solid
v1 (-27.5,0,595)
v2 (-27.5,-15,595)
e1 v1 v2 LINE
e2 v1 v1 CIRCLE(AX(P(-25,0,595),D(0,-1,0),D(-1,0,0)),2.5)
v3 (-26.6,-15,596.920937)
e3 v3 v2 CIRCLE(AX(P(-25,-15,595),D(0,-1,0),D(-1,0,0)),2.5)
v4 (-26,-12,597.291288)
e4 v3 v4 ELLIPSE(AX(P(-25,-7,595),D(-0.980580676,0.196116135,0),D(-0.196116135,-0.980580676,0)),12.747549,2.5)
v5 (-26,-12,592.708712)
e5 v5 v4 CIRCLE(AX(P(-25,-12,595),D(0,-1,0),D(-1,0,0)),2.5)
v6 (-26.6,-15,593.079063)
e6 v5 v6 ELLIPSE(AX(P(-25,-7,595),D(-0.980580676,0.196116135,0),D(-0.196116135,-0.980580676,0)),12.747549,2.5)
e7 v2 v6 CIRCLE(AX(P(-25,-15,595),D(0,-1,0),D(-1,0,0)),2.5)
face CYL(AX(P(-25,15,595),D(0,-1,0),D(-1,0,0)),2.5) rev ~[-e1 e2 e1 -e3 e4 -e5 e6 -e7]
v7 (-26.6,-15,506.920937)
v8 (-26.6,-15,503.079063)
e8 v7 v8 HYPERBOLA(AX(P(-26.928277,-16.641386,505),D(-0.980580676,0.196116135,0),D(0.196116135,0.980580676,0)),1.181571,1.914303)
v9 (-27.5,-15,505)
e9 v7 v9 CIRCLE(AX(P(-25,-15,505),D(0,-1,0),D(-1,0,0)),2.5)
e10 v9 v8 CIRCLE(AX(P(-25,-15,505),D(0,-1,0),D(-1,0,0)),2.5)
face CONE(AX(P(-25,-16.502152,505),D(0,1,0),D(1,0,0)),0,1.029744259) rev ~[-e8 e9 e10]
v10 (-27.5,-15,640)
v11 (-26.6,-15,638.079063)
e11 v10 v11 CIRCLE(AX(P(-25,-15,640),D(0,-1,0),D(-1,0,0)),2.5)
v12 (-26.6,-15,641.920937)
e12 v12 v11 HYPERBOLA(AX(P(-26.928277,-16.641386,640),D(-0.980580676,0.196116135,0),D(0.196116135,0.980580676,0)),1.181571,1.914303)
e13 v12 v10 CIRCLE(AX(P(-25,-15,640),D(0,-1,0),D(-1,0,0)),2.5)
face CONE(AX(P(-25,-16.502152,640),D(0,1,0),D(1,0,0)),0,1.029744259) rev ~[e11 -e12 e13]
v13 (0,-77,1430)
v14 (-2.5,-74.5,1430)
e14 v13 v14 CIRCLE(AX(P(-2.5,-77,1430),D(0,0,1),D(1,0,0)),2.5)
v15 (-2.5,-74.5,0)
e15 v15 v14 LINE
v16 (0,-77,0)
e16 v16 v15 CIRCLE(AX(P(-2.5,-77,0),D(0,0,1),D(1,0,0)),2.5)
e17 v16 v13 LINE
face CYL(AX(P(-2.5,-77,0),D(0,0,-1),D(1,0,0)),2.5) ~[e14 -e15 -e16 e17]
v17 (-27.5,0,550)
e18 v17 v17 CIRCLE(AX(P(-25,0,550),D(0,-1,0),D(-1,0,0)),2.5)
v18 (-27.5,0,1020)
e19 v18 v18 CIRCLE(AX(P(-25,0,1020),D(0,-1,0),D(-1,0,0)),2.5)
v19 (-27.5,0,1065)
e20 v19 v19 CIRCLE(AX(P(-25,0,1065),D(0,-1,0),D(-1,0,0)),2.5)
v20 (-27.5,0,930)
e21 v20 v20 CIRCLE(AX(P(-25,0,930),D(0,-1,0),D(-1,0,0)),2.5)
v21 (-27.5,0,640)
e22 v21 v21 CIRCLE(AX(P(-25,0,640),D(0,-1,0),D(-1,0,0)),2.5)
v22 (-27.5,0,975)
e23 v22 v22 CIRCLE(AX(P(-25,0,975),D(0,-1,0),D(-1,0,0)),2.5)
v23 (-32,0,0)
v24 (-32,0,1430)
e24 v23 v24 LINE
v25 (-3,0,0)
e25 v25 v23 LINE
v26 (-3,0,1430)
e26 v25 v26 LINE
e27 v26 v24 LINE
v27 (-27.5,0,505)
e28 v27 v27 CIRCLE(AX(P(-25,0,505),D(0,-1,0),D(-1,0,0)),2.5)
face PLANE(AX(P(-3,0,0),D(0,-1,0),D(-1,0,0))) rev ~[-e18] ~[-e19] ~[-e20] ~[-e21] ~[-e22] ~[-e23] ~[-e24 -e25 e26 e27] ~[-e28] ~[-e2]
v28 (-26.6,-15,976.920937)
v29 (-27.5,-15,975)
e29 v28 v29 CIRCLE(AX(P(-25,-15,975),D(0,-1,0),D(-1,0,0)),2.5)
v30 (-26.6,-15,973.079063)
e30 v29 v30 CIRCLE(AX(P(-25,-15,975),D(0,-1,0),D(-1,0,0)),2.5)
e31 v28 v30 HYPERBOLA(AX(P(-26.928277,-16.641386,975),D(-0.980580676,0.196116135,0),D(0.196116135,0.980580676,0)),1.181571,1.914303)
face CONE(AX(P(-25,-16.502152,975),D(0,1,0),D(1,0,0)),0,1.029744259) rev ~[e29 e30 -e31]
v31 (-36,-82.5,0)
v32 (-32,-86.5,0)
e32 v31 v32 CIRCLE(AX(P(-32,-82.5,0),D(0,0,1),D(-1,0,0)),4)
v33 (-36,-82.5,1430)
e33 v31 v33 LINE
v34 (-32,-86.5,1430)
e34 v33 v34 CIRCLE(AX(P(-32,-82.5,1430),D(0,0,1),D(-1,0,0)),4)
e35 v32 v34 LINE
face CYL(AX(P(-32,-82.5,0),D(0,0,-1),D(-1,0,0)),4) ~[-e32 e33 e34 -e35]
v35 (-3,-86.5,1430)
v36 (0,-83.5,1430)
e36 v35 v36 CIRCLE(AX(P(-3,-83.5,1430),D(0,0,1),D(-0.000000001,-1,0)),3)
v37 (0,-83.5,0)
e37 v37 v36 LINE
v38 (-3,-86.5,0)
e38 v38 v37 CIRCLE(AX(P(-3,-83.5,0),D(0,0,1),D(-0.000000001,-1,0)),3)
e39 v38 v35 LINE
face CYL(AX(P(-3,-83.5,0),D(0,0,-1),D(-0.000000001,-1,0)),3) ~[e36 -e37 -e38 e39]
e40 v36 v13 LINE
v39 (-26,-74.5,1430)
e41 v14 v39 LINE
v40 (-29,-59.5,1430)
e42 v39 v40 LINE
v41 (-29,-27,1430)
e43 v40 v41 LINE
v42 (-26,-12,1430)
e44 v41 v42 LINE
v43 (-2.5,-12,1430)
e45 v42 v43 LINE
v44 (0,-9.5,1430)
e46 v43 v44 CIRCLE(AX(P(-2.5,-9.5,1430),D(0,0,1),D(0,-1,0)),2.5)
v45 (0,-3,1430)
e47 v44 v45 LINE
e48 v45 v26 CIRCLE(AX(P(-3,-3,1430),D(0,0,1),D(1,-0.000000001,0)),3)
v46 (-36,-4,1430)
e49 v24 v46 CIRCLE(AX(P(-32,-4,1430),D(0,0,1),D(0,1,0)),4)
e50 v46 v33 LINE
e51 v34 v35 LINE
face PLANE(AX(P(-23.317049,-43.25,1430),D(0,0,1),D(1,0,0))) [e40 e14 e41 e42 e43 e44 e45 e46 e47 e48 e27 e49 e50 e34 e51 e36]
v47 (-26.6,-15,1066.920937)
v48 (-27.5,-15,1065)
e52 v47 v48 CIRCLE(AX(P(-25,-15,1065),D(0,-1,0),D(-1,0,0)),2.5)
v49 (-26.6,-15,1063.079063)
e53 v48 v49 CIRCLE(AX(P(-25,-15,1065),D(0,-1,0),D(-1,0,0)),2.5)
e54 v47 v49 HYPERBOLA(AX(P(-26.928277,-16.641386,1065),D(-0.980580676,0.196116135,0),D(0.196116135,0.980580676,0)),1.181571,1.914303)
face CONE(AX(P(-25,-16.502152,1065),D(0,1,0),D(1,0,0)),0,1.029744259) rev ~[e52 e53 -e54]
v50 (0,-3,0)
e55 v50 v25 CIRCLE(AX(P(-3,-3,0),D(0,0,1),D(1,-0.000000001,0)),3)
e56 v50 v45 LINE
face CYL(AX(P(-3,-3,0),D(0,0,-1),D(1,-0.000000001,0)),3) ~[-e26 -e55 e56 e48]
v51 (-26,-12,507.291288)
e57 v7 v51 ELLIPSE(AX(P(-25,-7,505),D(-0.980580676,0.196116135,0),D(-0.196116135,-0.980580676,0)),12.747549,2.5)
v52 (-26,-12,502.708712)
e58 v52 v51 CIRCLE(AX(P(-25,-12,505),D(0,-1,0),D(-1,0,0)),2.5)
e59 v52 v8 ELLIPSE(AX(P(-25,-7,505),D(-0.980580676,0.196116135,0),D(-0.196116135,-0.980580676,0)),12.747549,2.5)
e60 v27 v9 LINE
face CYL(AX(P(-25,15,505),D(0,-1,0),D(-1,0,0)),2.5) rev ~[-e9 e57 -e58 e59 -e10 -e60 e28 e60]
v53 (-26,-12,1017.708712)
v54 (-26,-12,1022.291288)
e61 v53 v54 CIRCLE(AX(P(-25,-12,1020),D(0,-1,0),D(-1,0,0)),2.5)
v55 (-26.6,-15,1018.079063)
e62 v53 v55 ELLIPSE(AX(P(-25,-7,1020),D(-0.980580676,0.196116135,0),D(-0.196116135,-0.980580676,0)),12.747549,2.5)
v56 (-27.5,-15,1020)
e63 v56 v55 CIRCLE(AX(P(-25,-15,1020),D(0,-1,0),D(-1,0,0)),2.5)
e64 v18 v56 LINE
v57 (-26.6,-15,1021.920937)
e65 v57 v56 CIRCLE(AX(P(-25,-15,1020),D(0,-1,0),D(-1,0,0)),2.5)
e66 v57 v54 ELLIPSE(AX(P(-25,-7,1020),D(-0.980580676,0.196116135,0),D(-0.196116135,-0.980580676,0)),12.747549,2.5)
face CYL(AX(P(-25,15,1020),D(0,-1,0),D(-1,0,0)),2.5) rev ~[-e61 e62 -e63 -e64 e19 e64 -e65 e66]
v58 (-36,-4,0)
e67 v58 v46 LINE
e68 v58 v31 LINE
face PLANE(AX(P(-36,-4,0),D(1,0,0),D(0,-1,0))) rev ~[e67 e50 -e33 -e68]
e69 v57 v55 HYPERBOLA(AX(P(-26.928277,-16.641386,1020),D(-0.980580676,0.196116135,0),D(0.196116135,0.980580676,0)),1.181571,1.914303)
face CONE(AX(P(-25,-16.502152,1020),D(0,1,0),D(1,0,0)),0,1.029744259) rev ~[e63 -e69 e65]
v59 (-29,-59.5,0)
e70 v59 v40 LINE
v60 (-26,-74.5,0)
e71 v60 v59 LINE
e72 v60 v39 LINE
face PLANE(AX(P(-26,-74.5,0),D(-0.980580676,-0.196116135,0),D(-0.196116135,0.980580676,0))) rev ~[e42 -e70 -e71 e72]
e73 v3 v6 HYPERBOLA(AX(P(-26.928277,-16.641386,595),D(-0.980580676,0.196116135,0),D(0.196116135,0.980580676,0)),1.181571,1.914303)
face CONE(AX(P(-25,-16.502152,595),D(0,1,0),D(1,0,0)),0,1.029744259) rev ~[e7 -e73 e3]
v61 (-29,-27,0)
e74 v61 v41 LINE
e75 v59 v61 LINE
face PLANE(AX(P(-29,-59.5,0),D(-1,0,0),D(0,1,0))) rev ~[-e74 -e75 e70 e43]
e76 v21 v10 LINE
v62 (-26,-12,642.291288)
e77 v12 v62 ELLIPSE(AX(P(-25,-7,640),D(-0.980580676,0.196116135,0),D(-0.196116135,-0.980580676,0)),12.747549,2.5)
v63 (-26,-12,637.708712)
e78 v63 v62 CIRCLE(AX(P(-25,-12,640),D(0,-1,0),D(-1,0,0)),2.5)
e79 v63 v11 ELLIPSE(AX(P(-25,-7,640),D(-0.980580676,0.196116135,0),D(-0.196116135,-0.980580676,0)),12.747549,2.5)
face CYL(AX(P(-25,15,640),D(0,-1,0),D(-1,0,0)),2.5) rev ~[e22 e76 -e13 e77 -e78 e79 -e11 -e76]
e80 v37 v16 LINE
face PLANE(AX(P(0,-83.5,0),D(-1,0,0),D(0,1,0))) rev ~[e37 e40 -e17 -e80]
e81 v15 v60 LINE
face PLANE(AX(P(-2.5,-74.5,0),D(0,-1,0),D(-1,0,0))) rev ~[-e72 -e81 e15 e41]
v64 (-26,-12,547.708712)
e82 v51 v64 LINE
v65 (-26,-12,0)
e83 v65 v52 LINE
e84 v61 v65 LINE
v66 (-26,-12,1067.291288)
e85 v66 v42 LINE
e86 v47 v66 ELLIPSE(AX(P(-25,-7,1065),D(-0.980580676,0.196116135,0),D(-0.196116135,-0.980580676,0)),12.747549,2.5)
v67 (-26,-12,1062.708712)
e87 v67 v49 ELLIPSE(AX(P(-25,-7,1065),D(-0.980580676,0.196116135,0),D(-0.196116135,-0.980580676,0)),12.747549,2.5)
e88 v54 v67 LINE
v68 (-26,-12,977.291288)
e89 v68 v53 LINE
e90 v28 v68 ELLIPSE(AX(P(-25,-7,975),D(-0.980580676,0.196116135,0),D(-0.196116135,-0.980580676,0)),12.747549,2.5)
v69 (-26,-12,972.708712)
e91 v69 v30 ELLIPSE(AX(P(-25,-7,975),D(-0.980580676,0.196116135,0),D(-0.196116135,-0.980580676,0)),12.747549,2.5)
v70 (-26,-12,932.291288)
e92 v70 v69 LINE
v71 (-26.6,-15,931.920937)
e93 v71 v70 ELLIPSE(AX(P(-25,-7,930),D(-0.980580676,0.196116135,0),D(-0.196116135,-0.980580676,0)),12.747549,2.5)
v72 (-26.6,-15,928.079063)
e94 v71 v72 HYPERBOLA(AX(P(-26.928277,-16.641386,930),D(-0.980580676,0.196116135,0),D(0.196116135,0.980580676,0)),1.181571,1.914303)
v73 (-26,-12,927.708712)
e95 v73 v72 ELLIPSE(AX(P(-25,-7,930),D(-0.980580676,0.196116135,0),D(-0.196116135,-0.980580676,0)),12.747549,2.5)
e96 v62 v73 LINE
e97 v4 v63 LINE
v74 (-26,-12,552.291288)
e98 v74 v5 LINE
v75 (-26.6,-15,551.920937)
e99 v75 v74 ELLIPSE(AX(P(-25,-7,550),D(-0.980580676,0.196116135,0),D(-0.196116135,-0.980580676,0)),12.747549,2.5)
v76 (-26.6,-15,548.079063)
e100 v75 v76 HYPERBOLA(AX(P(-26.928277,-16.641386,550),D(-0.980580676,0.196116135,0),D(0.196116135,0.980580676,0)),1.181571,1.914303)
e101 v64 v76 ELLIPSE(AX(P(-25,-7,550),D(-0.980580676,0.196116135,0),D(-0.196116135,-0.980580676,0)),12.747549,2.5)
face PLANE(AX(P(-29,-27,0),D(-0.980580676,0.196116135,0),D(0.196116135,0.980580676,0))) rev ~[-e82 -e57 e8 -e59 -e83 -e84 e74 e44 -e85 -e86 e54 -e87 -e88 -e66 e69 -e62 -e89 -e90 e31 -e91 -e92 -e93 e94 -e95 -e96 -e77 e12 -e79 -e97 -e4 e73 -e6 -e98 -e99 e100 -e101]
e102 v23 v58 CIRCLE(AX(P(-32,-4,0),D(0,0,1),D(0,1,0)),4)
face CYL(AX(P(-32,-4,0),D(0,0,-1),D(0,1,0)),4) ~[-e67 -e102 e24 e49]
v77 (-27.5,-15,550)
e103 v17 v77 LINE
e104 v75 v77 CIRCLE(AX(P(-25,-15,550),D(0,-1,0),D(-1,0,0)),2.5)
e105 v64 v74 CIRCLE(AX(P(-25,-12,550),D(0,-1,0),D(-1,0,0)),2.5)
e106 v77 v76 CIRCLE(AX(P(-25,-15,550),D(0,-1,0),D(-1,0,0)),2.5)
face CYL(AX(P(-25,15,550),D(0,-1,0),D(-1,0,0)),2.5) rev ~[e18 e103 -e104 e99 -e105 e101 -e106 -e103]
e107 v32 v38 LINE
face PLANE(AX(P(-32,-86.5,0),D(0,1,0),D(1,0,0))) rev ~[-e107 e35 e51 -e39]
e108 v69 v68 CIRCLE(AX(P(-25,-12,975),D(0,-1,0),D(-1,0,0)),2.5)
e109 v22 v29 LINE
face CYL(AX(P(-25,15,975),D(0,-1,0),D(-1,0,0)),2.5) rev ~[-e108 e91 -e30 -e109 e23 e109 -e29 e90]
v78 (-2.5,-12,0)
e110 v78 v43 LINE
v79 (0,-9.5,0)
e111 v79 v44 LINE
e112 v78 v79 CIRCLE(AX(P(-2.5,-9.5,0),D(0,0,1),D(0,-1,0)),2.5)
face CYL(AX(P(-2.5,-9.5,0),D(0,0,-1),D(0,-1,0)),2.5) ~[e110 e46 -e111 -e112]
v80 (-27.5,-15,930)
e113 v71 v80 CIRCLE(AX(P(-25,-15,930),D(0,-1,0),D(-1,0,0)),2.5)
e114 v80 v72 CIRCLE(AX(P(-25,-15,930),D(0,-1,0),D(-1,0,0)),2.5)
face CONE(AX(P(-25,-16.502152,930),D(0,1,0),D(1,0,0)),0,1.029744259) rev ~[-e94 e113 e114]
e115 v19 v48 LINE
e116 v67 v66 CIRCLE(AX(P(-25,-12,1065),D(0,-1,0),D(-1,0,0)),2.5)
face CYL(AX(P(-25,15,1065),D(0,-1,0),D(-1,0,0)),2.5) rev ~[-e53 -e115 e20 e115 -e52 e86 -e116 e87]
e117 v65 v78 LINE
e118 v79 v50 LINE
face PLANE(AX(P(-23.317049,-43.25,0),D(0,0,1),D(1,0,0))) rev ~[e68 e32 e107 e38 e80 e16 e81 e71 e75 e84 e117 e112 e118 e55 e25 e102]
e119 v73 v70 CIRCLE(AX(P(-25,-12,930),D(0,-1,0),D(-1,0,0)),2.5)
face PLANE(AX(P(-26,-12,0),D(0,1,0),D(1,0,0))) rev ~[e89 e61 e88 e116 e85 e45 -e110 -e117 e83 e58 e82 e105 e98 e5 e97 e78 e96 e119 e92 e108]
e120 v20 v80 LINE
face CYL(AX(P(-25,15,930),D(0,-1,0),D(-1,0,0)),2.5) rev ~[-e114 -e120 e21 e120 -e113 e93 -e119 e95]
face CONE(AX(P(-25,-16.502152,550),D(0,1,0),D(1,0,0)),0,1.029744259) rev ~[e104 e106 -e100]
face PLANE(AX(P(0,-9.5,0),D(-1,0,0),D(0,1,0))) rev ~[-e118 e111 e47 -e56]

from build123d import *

# Parameters (mm, degrees)
BOSS_EXTRUDE1_DEPTH   = 1430
M6_TAPPED_HOLE1_D     = 5
M6_TAPPED_HOLE1_DEPTH = 15
M6_TAPPED_HOLE1_TIP   = 1.502151548


with BuildPart() as part:
    # Sketch1 → Boss-Extrude1 (new body)
    with BuildSketch(Plane.XY):
        with BuildLine():
            Line((-3, 0), (-32, 0))
            ThreePointArc((-32, 0), (-34.828427125, -1.171572875), (-36, -4))
            Line((-36, -4), (-36, -82.5))
            ThreePointArc((-36, -82.5), (-34.828427125, -85.328427125), (-32, -86.5))
            Line((-32, -86.5), (-3, -86.5))
            ThreePointArc((-3, -86.5), (-0.878679656, -85.621320344), (0, -83.5))
            Line((0, -83.5), (0, -77))
            ThreePointArc((0, -77), (-0.732233047, -75.232233047), (-2.5, -74.5))
            Line((-2.5, -74.5), (-26, -74.5))
            Line((-26, -74.5), (-29, -59.5))
            Line((-29, -59.5), (-29, -27))
            Line((-29, -27), (-26, -12))
            Line((-26, -12), (-2.5, -12))
            ThreePointArc((-2.5, -12), (-0.732233047, -11.267766953), (0, -9.5))
            Line((0, -9.5), (0, -3))
            ThreePointArc((0, -3), (-0.878679656, -0.878679656), (-3, 0))
        make_face()
    extrude(amount=BOSS_EXTRUDE1_DEPTH)

    # M6 Tapped Hole1
    with Locations(Plane(origin=(0, 0, 0), x_dir=(1, 0, 0), z_dir=(0, 1, 0))):
        with Locations((-25, -505), (-25, -550), (-25, -595), (-25, -640), (-25, -930), (-25, -975), (-25, -1020), (-25, -1065)):
            Hole(M6_TAPPED_HOLE1_D / 2, depth=M6_TAPPED_HOLE1_DEPTH)
            with Locations((0, 0, -(M6_TAPPED_HOLE1_DEPTH + M6_TAPPED_HOLE1_TIP / 2))):  # 118° drill point
                Cone(0, M6_TAPPED_HOLE1_D / 2, M6_TAPPED_HOLE1_TIP, mode=Mode.SUBTRACT)


solid = part.part
